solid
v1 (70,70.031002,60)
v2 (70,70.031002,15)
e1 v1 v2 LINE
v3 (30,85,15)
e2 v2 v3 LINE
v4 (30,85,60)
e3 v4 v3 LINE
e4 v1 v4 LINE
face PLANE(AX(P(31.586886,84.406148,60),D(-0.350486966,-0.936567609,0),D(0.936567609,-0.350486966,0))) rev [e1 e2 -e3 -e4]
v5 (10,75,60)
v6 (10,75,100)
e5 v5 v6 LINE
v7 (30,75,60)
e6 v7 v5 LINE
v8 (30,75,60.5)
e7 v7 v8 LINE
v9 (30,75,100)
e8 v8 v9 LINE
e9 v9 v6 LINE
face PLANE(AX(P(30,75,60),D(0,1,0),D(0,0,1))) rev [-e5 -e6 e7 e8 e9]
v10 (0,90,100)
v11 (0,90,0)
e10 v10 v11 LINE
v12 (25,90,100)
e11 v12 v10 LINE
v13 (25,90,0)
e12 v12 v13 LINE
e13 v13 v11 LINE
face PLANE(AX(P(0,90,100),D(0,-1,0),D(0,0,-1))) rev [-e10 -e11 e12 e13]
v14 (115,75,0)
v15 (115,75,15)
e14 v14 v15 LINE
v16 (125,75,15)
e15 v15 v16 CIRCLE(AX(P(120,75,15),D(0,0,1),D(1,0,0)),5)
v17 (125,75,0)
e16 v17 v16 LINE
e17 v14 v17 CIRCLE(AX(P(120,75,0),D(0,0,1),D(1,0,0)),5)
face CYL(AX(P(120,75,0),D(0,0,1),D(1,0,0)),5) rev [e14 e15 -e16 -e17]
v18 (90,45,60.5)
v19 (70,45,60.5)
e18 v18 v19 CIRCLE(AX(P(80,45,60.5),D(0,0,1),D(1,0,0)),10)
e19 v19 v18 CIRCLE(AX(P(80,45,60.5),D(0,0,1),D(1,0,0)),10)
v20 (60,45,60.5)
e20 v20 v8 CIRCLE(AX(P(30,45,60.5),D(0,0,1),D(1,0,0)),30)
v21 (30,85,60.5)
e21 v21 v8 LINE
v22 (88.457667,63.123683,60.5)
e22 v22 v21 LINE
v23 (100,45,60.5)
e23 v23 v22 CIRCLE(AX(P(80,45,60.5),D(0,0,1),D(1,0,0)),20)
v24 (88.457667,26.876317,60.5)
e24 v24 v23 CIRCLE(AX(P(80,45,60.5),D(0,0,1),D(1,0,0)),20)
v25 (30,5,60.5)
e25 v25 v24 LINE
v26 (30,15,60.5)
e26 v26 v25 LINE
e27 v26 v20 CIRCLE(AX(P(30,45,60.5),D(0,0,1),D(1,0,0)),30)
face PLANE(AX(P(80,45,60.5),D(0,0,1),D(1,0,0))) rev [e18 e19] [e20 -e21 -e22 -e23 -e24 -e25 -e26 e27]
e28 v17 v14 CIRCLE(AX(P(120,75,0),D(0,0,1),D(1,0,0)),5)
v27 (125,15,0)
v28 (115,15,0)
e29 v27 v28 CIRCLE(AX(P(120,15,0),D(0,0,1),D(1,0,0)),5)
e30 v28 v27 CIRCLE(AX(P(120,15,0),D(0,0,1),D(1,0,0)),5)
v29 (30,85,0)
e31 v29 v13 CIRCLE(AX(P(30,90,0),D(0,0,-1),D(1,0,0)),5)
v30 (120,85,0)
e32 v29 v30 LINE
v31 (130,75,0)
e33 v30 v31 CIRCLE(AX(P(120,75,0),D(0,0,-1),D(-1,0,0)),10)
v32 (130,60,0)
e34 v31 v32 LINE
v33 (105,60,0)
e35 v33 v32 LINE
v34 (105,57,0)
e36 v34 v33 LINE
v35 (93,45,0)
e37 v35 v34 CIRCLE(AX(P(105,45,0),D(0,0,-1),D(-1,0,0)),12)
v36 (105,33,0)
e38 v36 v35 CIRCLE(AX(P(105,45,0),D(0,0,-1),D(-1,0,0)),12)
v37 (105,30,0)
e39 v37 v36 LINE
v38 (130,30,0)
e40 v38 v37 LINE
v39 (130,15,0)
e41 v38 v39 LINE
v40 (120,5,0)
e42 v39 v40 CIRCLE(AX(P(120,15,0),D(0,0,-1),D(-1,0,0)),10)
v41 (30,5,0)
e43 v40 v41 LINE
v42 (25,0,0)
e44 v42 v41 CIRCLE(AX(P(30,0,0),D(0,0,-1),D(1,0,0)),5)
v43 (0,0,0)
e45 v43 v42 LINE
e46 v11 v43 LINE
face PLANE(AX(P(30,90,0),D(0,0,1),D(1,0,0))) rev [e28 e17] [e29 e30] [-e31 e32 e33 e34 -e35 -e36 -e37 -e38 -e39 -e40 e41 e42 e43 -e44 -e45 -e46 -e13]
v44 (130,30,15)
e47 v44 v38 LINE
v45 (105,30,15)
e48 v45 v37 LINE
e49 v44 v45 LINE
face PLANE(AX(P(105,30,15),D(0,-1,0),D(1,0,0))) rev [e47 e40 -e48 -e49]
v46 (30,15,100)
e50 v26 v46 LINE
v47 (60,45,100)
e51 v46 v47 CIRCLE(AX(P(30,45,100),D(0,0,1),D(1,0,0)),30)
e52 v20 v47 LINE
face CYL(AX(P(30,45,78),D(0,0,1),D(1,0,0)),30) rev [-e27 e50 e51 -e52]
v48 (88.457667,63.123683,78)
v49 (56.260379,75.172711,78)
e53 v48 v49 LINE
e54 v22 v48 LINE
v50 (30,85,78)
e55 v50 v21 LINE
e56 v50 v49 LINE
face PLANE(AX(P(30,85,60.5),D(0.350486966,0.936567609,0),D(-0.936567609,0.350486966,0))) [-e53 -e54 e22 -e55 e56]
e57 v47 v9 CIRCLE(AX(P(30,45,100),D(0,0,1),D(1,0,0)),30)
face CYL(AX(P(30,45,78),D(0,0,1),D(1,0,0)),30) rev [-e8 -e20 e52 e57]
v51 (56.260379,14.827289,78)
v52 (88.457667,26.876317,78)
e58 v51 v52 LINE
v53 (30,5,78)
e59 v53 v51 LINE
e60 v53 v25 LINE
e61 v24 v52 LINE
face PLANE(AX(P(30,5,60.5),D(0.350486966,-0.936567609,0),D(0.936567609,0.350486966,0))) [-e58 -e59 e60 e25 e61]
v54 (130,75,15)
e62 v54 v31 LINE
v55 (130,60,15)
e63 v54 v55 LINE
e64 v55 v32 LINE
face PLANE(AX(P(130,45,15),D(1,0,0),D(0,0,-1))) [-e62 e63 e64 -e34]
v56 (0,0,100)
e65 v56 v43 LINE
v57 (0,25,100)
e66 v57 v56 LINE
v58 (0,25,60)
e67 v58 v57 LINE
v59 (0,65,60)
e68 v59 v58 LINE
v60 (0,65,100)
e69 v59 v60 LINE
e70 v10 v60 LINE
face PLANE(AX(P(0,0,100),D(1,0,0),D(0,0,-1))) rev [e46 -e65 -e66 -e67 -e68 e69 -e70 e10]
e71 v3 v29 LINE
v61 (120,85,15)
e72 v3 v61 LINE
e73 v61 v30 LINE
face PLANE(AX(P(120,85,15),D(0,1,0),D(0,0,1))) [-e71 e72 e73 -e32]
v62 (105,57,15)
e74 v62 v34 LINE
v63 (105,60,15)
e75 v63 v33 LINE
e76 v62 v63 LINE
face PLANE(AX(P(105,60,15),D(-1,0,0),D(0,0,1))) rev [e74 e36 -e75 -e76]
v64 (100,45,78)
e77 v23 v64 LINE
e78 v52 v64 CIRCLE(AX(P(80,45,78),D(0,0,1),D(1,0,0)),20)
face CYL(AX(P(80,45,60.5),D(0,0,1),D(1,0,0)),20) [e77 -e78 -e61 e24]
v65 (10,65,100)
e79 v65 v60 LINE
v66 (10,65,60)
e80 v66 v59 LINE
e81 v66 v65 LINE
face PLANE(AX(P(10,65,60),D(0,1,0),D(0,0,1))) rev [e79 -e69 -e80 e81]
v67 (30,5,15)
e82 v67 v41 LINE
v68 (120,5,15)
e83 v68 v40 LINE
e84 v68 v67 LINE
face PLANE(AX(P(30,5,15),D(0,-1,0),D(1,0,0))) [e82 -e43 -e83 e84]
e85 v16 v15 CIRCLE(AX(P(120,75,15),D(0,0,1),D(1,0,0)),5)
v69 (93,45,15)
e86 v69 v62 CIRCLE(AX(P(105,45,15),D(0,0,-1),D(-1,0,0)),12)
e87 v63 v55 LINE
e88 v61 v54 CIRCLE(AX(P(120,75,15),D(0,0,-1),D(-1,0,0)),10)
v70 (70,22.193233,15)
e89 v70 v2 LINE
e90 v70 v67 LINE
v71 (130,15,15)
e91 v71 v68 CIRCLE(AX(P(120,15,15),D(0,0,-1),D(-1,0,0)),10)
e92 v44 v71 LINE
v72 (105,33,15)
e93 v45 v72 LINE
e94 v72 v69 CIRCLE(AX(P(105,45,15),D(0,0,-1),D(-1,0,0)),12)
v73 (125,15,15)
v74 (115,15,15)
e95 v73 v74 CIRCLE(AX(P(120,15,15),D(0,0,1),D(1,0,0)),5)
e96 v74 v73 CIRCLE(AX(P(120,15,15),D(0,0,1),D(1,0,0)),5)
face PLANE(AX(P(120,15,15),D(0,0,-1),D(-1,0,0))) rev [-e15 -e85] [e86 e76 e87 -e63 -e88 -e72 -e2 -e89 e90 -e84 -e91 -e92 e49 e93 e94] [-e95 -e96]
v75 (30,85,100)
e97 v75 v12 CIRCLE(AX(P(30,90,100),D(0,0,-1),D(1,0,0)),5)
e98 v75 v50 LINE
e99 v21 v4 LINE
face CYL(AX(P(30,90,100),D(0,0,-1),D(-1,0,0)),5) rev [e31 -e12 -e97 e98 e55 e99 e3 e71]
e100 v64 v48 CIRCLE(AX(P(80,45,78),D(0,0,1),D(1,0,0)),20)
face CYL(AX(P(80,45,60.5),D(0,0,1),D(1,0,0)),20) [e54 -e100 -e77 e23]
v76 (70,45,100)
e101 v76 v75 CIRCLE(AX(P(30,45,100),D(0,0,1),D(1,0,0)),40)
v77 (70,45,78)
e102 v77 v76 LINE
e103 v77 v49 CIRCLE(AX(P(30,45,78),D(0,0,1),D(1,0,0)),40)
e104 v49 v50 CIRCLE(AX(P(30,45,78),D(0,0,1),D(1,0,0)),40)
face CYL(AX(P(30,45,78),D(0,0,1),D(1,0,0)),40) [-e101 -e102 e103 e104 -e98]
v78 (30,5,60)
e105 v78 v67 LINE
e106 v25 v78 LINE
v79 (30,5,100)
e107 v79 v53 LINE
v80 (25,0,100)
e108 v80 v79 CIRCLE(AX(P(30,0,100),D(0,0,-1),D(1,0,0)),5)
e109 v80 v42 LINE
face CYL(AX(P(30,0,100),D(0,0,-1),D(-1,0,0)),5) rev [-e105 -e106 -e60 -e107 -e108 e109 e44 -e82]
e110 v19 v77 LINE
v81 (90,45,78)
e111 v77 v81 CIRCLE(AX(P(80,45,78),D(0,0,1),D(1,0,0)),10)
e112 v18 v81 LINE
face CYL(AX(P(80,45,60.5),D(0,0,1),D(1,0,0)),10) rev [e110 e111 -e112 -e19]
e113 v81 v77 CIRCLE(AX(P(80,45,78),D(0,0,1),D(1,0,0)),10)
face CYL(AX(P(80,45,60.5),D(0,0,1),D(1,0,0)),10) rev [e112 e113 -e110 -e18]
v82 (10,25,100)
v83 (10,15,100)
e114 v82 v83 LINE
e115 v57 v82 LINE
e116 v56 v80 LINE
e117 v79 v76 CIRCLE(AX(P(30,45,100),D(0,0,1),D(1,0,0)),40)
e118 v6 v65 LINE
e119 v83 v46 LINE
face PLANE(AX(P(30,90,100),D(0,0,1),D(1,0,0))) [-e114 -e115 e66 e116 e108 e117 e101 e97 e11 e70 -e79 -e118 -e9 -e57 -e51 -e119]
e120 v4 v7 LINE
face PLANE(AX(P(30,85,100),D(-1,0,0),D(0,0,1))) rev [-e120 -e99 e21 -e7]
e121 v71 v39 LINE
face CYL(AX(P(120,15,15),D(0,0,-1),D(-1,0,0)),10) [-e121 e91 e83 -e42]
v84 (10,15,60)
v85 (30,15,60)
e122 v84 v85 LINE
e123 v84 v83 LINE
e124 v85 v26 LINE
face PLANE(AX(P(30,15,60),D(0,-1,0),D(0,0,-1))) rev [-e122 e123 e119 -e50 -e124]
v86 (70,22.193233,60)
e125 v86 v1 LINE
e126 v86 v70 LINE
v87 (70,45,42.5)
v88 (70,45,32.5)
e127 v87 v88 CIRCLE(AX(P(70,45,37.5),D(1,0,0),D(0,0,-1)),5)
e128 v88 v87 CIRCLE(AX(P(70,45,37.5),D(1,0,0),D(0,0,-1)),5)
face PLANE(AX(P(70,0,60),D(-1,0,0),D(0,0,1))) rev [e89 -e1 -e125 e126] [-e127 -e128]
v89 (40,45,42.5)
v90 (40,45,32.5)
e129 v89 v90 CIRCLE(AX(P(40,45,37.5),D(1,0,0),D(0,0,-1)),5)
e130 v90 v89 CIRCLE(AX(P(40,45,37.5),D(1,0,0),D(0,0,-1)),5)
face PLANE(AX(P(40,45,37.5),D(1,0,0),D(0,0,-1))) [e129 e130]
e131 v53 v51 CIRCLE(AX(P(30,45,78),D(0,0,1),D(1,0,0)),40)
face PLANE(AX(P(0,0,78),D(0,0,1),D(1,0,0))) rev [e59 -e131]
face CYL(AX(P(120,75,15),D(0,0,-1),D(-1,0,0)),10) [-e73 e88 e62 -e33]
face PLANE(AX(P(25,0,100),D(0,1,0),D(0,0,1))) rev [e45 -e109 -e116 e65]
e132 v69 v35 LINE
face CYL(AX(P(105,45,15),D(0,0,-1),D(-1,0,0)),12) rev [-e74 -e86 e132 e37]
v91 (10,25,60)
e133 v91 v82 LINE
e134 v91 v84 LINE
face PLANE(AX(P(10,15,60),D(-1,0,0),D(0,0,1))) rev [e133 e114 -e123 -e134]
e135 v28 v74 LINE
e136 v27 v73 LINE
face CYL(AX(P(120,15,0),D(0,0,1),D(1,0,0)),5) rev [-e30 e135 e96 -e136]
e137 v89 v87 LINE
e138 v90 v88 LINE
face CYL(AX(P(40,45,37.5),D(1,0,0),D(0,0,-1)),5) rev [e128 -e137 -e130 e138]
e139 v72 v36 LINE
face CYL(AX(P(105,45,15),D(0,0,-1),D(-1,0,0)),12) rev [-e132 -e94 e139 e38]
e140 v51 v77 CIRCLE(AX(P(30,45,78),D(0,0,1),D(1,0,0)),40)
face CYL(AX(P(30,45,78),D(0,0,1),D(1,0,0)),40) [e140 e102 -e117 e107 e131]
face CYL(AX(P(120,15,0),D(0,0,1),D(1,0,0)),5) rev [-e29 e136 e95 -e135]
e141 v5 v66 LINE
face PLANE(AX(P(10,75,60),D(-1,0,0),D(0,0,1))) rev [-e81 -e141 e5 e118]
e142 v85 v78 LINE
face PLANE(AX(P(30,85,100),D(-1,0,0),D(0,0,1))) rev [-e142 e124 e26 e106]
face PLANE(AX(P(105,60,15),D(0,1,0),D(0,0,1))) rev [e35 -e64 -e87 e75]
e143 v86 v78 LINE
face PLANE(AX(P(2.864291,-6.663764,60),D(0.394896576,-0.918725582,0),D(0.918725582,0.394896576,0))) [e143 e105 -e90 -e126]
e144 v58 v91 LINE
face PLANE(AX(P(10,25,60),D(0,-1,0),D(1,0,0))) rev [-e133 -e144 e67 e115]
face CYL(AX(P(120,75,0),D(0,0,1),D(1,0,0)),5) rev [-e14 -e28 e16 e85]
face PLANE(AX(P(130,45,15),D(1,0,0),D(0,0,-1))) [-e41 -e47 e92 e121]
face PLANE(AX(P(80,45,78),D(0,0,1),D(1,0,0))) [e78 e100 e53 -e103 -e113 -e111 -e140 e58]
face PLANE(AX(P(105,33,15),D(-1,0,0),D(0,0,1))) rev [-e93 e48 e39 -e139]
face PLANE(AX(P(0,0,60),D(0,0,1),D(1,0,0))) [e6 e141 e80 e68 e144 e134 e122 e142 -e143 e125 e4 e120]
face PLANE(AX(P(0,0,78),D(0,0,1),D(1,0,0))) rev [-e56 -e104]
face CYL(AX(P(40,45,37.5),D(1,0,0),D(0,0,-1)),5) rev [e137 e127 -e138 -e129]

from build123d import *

# Parameters (mm, degrees)
BASE_BODY_DEPTH         = 100
MOUNTING_FLANGE_DEPTH   = 15
FLANGE_HOLES_CUT_DEPTH  = 15
FLANGE_NOTCH_PROFILE_R  = 5
FLANGE_NOTCH_CUT_DEPTH  = 15
HOUSING_BLOCK_DEPTH     = 39.5
HOUSING_RECESS_DEPTH    = 22
PIVOT_BOSS_DEPTH        = 45
SIDE_PIN_HOLE_PROFILE_R = 10
SIDE_PIN_HOLE_DEPTH     = 17.5
PIVOT_BORE_PROFILE_R    = 5
PIVOT_BORE_DEPTH        = 30
BEARING_HOUSING_DEPTH   = 22
BEARING_BORE_DEPTH      = 40


with BuildPart() as part:
    # Base Body Profile → Base Body (new body)
    with BuildSketch(Plane.XY):
        with BuildLine():
            Line((0, 0), (0, 90))
            Line((0, 90), (25, 90))
            ThreePointArc((25, 90), (26.464466094, 86.464466094), (30, 85))
            Line((30, 85), (30, 5))
            ThreePointArc((30, 5), (26.464466094, 3.535533906), (25, 0))
            Line((25, 0), (0, 0))
        make_face()
    extrude(amount=BASE_BODY_DEPTH)

    # Mounting Flange Profile → Mounting Flange (add)
    with BuildSketch(Plane(origin=(0, 0, 0), x_dir=(-1, 0, 0), z_dir=(0, 0, -1))):
        with BuildLine():
            Line((-130, 45), (-130, 75))
            ThreePointArc((-130, 75), (-127.071067812, 82.071067812), (-120, 85))
            Line((-120, 85), (-30, 85))
            Line((-30, 85), (-30, 5))
            Line((-30, 5), (-120, 5))
            ThreePointArc((-120, 5), (-127.071067812, 7.928932188), (-130, 15))
            Line((-130, 15), (-130, 45))
        make_face()
    extrude(amount=-MOUNTING_FLANGE_DEPTH)

    # Flange Holes Profile → Flange Holes Cut (cut)
    with BuildSketch(Plane(origin=(0, 0, 0), x_dir=(-1, 0, 0), z_dir=(0, 0, -1))):
        with BuildLine():
            Line((-130, 60), (-130, 30))
            Line((-130, 30), (-105, 30))
            Line((-105, 30), (-105, 33))
            ThreePointArc((-105, 33), (-93, 45), (-105, 57))
            Line((-105, 57), (-105, 60))
            Line((-105, 60), (-130, 60))
        make_face()
    extrude(amount=-FLANGE_HOLES_CUT_DEPTH, mode=Mode.SUBTRACT)

    # Flange Notch Profile → Flange Notch Cut (cut)
    with BuildSketch(Plane.XY.offset(15)):
        with Locations((120, 75)):
            Circle(FLANGE_NOTCH_PROFILE_R)
        with Locations((120, 15)):
            Circle(FLANGE_NOTCH_PROFILE_R)
    extrude(amount=-FLANGE_NOTCH_CUT_DEPTH, mode=Mode.SUBTRACT)

    # Housing Block Profile → Housing Block (add)
    with BuildSketch(Plane.XY.offset(100)):
        with BuildLine():
            Line((30, 85), (88.457666717, 63.123682675))
            ThreePointArc((88.457666717, 63.123682675), (100, 45), (88.457666717, 26.876317325))
            Line((88.457666717, 26.876317325), (30, 5))
            Line((30, 5), (30, 85))
        make_face()
    extrude(amount=-HOUSING_BLOCK_DEPTH)

    # Housing Recess Profile → Housing Recess (cut)
    with BuildSketch(Plane.XY.offset(100)):
        with BuildLine():
            Line((30, 85), (30, 5))
            Line((30, 5), (88.457666717, 26.876317325))
            ThreePointArc((88.457666717, 26.876317325), (100, 45), (88.457666717, 63.123682675))
            Line((88.457666717, 63.123682675), (30, 85))
        make_face()
    extrude(amount=-HOUSING_RECESS_DEPTH, mode=Mode.SUBTRACT)

    # Pivot Boss Profile → Pivot Boss (add)
    with BuildSketch(Plane.XY.offset(15)):
        Polygon((70, 70.031002054), (30, 85), (30, 45), (70, 45), align=None)
        Polygon((70, 45), (30, 45), (30, 5), (70, 22.19323305), align=None)
    extrude(amount=PIVOT_BOSS_DEPTH)

    # Side Pin Hole Profile → Side Pin Hole (cut)
    with BuildSketch(Plane.XY.offset(78)):
        with Locations((80, 45)):
            Circle(SIDE_PIN_HOLE_PROFILE_R)
    extrude(amount=-SIDE_PIN_HOLE_DEPTH, mode=Mode.SUBTRACT)

    # Pivot Bore Profile → Pivot Bore (cut)
    with BuildSketch(Plane(origin=(70, 0, 0), x_dir=(0, 0, -1), z_dir=(1, 0, 0))):
        with Locations((-37.5, 45)):
            Circle(PIVOT_BORE_PROFILE_R)
    extrude(amount=-PIVOT_BORE_DEPTH, mode=Mode.SUBTRACT)

    # Bearing Housing Profile → Bearing Housing (add)
    with BuildSketch(Plane.XY.offset(100)):
        with BuildLine():
            ThreePointArc((30, 5), (70, 45), (30, 85))
            Line((30, 85), (30, 75))
            ThreePointArc((30, 75), (60, 45), (30, 15))
            Line((30, 15), (30, 5))
        make_face()
    extrude(amount=-BEARING_HOUSING_DEPTH)

    # Bearing Bore Profile → Bearing Bore (cut)
    with BuildSketch(Plane.XY.offset(100)):
        with BuildLine():
            Line((30, 75), (10, 75))
            Line((10, 75), (10, 65))
            Line((10, 65), (0, 65))
            Line((0, 65), (0, 25))
            Line((0, 25), (10, 25))
            Line((10, 25), (10, 15))
            Line((10, 15), (30, 15))
            ThreePointArc((30, 15), (60, 45), (30, 75))
        make_face()
    extrude(amount=-BEARING_BORE_DEPTH, mode=Mode.SUBTRACT)


solid = part.part
